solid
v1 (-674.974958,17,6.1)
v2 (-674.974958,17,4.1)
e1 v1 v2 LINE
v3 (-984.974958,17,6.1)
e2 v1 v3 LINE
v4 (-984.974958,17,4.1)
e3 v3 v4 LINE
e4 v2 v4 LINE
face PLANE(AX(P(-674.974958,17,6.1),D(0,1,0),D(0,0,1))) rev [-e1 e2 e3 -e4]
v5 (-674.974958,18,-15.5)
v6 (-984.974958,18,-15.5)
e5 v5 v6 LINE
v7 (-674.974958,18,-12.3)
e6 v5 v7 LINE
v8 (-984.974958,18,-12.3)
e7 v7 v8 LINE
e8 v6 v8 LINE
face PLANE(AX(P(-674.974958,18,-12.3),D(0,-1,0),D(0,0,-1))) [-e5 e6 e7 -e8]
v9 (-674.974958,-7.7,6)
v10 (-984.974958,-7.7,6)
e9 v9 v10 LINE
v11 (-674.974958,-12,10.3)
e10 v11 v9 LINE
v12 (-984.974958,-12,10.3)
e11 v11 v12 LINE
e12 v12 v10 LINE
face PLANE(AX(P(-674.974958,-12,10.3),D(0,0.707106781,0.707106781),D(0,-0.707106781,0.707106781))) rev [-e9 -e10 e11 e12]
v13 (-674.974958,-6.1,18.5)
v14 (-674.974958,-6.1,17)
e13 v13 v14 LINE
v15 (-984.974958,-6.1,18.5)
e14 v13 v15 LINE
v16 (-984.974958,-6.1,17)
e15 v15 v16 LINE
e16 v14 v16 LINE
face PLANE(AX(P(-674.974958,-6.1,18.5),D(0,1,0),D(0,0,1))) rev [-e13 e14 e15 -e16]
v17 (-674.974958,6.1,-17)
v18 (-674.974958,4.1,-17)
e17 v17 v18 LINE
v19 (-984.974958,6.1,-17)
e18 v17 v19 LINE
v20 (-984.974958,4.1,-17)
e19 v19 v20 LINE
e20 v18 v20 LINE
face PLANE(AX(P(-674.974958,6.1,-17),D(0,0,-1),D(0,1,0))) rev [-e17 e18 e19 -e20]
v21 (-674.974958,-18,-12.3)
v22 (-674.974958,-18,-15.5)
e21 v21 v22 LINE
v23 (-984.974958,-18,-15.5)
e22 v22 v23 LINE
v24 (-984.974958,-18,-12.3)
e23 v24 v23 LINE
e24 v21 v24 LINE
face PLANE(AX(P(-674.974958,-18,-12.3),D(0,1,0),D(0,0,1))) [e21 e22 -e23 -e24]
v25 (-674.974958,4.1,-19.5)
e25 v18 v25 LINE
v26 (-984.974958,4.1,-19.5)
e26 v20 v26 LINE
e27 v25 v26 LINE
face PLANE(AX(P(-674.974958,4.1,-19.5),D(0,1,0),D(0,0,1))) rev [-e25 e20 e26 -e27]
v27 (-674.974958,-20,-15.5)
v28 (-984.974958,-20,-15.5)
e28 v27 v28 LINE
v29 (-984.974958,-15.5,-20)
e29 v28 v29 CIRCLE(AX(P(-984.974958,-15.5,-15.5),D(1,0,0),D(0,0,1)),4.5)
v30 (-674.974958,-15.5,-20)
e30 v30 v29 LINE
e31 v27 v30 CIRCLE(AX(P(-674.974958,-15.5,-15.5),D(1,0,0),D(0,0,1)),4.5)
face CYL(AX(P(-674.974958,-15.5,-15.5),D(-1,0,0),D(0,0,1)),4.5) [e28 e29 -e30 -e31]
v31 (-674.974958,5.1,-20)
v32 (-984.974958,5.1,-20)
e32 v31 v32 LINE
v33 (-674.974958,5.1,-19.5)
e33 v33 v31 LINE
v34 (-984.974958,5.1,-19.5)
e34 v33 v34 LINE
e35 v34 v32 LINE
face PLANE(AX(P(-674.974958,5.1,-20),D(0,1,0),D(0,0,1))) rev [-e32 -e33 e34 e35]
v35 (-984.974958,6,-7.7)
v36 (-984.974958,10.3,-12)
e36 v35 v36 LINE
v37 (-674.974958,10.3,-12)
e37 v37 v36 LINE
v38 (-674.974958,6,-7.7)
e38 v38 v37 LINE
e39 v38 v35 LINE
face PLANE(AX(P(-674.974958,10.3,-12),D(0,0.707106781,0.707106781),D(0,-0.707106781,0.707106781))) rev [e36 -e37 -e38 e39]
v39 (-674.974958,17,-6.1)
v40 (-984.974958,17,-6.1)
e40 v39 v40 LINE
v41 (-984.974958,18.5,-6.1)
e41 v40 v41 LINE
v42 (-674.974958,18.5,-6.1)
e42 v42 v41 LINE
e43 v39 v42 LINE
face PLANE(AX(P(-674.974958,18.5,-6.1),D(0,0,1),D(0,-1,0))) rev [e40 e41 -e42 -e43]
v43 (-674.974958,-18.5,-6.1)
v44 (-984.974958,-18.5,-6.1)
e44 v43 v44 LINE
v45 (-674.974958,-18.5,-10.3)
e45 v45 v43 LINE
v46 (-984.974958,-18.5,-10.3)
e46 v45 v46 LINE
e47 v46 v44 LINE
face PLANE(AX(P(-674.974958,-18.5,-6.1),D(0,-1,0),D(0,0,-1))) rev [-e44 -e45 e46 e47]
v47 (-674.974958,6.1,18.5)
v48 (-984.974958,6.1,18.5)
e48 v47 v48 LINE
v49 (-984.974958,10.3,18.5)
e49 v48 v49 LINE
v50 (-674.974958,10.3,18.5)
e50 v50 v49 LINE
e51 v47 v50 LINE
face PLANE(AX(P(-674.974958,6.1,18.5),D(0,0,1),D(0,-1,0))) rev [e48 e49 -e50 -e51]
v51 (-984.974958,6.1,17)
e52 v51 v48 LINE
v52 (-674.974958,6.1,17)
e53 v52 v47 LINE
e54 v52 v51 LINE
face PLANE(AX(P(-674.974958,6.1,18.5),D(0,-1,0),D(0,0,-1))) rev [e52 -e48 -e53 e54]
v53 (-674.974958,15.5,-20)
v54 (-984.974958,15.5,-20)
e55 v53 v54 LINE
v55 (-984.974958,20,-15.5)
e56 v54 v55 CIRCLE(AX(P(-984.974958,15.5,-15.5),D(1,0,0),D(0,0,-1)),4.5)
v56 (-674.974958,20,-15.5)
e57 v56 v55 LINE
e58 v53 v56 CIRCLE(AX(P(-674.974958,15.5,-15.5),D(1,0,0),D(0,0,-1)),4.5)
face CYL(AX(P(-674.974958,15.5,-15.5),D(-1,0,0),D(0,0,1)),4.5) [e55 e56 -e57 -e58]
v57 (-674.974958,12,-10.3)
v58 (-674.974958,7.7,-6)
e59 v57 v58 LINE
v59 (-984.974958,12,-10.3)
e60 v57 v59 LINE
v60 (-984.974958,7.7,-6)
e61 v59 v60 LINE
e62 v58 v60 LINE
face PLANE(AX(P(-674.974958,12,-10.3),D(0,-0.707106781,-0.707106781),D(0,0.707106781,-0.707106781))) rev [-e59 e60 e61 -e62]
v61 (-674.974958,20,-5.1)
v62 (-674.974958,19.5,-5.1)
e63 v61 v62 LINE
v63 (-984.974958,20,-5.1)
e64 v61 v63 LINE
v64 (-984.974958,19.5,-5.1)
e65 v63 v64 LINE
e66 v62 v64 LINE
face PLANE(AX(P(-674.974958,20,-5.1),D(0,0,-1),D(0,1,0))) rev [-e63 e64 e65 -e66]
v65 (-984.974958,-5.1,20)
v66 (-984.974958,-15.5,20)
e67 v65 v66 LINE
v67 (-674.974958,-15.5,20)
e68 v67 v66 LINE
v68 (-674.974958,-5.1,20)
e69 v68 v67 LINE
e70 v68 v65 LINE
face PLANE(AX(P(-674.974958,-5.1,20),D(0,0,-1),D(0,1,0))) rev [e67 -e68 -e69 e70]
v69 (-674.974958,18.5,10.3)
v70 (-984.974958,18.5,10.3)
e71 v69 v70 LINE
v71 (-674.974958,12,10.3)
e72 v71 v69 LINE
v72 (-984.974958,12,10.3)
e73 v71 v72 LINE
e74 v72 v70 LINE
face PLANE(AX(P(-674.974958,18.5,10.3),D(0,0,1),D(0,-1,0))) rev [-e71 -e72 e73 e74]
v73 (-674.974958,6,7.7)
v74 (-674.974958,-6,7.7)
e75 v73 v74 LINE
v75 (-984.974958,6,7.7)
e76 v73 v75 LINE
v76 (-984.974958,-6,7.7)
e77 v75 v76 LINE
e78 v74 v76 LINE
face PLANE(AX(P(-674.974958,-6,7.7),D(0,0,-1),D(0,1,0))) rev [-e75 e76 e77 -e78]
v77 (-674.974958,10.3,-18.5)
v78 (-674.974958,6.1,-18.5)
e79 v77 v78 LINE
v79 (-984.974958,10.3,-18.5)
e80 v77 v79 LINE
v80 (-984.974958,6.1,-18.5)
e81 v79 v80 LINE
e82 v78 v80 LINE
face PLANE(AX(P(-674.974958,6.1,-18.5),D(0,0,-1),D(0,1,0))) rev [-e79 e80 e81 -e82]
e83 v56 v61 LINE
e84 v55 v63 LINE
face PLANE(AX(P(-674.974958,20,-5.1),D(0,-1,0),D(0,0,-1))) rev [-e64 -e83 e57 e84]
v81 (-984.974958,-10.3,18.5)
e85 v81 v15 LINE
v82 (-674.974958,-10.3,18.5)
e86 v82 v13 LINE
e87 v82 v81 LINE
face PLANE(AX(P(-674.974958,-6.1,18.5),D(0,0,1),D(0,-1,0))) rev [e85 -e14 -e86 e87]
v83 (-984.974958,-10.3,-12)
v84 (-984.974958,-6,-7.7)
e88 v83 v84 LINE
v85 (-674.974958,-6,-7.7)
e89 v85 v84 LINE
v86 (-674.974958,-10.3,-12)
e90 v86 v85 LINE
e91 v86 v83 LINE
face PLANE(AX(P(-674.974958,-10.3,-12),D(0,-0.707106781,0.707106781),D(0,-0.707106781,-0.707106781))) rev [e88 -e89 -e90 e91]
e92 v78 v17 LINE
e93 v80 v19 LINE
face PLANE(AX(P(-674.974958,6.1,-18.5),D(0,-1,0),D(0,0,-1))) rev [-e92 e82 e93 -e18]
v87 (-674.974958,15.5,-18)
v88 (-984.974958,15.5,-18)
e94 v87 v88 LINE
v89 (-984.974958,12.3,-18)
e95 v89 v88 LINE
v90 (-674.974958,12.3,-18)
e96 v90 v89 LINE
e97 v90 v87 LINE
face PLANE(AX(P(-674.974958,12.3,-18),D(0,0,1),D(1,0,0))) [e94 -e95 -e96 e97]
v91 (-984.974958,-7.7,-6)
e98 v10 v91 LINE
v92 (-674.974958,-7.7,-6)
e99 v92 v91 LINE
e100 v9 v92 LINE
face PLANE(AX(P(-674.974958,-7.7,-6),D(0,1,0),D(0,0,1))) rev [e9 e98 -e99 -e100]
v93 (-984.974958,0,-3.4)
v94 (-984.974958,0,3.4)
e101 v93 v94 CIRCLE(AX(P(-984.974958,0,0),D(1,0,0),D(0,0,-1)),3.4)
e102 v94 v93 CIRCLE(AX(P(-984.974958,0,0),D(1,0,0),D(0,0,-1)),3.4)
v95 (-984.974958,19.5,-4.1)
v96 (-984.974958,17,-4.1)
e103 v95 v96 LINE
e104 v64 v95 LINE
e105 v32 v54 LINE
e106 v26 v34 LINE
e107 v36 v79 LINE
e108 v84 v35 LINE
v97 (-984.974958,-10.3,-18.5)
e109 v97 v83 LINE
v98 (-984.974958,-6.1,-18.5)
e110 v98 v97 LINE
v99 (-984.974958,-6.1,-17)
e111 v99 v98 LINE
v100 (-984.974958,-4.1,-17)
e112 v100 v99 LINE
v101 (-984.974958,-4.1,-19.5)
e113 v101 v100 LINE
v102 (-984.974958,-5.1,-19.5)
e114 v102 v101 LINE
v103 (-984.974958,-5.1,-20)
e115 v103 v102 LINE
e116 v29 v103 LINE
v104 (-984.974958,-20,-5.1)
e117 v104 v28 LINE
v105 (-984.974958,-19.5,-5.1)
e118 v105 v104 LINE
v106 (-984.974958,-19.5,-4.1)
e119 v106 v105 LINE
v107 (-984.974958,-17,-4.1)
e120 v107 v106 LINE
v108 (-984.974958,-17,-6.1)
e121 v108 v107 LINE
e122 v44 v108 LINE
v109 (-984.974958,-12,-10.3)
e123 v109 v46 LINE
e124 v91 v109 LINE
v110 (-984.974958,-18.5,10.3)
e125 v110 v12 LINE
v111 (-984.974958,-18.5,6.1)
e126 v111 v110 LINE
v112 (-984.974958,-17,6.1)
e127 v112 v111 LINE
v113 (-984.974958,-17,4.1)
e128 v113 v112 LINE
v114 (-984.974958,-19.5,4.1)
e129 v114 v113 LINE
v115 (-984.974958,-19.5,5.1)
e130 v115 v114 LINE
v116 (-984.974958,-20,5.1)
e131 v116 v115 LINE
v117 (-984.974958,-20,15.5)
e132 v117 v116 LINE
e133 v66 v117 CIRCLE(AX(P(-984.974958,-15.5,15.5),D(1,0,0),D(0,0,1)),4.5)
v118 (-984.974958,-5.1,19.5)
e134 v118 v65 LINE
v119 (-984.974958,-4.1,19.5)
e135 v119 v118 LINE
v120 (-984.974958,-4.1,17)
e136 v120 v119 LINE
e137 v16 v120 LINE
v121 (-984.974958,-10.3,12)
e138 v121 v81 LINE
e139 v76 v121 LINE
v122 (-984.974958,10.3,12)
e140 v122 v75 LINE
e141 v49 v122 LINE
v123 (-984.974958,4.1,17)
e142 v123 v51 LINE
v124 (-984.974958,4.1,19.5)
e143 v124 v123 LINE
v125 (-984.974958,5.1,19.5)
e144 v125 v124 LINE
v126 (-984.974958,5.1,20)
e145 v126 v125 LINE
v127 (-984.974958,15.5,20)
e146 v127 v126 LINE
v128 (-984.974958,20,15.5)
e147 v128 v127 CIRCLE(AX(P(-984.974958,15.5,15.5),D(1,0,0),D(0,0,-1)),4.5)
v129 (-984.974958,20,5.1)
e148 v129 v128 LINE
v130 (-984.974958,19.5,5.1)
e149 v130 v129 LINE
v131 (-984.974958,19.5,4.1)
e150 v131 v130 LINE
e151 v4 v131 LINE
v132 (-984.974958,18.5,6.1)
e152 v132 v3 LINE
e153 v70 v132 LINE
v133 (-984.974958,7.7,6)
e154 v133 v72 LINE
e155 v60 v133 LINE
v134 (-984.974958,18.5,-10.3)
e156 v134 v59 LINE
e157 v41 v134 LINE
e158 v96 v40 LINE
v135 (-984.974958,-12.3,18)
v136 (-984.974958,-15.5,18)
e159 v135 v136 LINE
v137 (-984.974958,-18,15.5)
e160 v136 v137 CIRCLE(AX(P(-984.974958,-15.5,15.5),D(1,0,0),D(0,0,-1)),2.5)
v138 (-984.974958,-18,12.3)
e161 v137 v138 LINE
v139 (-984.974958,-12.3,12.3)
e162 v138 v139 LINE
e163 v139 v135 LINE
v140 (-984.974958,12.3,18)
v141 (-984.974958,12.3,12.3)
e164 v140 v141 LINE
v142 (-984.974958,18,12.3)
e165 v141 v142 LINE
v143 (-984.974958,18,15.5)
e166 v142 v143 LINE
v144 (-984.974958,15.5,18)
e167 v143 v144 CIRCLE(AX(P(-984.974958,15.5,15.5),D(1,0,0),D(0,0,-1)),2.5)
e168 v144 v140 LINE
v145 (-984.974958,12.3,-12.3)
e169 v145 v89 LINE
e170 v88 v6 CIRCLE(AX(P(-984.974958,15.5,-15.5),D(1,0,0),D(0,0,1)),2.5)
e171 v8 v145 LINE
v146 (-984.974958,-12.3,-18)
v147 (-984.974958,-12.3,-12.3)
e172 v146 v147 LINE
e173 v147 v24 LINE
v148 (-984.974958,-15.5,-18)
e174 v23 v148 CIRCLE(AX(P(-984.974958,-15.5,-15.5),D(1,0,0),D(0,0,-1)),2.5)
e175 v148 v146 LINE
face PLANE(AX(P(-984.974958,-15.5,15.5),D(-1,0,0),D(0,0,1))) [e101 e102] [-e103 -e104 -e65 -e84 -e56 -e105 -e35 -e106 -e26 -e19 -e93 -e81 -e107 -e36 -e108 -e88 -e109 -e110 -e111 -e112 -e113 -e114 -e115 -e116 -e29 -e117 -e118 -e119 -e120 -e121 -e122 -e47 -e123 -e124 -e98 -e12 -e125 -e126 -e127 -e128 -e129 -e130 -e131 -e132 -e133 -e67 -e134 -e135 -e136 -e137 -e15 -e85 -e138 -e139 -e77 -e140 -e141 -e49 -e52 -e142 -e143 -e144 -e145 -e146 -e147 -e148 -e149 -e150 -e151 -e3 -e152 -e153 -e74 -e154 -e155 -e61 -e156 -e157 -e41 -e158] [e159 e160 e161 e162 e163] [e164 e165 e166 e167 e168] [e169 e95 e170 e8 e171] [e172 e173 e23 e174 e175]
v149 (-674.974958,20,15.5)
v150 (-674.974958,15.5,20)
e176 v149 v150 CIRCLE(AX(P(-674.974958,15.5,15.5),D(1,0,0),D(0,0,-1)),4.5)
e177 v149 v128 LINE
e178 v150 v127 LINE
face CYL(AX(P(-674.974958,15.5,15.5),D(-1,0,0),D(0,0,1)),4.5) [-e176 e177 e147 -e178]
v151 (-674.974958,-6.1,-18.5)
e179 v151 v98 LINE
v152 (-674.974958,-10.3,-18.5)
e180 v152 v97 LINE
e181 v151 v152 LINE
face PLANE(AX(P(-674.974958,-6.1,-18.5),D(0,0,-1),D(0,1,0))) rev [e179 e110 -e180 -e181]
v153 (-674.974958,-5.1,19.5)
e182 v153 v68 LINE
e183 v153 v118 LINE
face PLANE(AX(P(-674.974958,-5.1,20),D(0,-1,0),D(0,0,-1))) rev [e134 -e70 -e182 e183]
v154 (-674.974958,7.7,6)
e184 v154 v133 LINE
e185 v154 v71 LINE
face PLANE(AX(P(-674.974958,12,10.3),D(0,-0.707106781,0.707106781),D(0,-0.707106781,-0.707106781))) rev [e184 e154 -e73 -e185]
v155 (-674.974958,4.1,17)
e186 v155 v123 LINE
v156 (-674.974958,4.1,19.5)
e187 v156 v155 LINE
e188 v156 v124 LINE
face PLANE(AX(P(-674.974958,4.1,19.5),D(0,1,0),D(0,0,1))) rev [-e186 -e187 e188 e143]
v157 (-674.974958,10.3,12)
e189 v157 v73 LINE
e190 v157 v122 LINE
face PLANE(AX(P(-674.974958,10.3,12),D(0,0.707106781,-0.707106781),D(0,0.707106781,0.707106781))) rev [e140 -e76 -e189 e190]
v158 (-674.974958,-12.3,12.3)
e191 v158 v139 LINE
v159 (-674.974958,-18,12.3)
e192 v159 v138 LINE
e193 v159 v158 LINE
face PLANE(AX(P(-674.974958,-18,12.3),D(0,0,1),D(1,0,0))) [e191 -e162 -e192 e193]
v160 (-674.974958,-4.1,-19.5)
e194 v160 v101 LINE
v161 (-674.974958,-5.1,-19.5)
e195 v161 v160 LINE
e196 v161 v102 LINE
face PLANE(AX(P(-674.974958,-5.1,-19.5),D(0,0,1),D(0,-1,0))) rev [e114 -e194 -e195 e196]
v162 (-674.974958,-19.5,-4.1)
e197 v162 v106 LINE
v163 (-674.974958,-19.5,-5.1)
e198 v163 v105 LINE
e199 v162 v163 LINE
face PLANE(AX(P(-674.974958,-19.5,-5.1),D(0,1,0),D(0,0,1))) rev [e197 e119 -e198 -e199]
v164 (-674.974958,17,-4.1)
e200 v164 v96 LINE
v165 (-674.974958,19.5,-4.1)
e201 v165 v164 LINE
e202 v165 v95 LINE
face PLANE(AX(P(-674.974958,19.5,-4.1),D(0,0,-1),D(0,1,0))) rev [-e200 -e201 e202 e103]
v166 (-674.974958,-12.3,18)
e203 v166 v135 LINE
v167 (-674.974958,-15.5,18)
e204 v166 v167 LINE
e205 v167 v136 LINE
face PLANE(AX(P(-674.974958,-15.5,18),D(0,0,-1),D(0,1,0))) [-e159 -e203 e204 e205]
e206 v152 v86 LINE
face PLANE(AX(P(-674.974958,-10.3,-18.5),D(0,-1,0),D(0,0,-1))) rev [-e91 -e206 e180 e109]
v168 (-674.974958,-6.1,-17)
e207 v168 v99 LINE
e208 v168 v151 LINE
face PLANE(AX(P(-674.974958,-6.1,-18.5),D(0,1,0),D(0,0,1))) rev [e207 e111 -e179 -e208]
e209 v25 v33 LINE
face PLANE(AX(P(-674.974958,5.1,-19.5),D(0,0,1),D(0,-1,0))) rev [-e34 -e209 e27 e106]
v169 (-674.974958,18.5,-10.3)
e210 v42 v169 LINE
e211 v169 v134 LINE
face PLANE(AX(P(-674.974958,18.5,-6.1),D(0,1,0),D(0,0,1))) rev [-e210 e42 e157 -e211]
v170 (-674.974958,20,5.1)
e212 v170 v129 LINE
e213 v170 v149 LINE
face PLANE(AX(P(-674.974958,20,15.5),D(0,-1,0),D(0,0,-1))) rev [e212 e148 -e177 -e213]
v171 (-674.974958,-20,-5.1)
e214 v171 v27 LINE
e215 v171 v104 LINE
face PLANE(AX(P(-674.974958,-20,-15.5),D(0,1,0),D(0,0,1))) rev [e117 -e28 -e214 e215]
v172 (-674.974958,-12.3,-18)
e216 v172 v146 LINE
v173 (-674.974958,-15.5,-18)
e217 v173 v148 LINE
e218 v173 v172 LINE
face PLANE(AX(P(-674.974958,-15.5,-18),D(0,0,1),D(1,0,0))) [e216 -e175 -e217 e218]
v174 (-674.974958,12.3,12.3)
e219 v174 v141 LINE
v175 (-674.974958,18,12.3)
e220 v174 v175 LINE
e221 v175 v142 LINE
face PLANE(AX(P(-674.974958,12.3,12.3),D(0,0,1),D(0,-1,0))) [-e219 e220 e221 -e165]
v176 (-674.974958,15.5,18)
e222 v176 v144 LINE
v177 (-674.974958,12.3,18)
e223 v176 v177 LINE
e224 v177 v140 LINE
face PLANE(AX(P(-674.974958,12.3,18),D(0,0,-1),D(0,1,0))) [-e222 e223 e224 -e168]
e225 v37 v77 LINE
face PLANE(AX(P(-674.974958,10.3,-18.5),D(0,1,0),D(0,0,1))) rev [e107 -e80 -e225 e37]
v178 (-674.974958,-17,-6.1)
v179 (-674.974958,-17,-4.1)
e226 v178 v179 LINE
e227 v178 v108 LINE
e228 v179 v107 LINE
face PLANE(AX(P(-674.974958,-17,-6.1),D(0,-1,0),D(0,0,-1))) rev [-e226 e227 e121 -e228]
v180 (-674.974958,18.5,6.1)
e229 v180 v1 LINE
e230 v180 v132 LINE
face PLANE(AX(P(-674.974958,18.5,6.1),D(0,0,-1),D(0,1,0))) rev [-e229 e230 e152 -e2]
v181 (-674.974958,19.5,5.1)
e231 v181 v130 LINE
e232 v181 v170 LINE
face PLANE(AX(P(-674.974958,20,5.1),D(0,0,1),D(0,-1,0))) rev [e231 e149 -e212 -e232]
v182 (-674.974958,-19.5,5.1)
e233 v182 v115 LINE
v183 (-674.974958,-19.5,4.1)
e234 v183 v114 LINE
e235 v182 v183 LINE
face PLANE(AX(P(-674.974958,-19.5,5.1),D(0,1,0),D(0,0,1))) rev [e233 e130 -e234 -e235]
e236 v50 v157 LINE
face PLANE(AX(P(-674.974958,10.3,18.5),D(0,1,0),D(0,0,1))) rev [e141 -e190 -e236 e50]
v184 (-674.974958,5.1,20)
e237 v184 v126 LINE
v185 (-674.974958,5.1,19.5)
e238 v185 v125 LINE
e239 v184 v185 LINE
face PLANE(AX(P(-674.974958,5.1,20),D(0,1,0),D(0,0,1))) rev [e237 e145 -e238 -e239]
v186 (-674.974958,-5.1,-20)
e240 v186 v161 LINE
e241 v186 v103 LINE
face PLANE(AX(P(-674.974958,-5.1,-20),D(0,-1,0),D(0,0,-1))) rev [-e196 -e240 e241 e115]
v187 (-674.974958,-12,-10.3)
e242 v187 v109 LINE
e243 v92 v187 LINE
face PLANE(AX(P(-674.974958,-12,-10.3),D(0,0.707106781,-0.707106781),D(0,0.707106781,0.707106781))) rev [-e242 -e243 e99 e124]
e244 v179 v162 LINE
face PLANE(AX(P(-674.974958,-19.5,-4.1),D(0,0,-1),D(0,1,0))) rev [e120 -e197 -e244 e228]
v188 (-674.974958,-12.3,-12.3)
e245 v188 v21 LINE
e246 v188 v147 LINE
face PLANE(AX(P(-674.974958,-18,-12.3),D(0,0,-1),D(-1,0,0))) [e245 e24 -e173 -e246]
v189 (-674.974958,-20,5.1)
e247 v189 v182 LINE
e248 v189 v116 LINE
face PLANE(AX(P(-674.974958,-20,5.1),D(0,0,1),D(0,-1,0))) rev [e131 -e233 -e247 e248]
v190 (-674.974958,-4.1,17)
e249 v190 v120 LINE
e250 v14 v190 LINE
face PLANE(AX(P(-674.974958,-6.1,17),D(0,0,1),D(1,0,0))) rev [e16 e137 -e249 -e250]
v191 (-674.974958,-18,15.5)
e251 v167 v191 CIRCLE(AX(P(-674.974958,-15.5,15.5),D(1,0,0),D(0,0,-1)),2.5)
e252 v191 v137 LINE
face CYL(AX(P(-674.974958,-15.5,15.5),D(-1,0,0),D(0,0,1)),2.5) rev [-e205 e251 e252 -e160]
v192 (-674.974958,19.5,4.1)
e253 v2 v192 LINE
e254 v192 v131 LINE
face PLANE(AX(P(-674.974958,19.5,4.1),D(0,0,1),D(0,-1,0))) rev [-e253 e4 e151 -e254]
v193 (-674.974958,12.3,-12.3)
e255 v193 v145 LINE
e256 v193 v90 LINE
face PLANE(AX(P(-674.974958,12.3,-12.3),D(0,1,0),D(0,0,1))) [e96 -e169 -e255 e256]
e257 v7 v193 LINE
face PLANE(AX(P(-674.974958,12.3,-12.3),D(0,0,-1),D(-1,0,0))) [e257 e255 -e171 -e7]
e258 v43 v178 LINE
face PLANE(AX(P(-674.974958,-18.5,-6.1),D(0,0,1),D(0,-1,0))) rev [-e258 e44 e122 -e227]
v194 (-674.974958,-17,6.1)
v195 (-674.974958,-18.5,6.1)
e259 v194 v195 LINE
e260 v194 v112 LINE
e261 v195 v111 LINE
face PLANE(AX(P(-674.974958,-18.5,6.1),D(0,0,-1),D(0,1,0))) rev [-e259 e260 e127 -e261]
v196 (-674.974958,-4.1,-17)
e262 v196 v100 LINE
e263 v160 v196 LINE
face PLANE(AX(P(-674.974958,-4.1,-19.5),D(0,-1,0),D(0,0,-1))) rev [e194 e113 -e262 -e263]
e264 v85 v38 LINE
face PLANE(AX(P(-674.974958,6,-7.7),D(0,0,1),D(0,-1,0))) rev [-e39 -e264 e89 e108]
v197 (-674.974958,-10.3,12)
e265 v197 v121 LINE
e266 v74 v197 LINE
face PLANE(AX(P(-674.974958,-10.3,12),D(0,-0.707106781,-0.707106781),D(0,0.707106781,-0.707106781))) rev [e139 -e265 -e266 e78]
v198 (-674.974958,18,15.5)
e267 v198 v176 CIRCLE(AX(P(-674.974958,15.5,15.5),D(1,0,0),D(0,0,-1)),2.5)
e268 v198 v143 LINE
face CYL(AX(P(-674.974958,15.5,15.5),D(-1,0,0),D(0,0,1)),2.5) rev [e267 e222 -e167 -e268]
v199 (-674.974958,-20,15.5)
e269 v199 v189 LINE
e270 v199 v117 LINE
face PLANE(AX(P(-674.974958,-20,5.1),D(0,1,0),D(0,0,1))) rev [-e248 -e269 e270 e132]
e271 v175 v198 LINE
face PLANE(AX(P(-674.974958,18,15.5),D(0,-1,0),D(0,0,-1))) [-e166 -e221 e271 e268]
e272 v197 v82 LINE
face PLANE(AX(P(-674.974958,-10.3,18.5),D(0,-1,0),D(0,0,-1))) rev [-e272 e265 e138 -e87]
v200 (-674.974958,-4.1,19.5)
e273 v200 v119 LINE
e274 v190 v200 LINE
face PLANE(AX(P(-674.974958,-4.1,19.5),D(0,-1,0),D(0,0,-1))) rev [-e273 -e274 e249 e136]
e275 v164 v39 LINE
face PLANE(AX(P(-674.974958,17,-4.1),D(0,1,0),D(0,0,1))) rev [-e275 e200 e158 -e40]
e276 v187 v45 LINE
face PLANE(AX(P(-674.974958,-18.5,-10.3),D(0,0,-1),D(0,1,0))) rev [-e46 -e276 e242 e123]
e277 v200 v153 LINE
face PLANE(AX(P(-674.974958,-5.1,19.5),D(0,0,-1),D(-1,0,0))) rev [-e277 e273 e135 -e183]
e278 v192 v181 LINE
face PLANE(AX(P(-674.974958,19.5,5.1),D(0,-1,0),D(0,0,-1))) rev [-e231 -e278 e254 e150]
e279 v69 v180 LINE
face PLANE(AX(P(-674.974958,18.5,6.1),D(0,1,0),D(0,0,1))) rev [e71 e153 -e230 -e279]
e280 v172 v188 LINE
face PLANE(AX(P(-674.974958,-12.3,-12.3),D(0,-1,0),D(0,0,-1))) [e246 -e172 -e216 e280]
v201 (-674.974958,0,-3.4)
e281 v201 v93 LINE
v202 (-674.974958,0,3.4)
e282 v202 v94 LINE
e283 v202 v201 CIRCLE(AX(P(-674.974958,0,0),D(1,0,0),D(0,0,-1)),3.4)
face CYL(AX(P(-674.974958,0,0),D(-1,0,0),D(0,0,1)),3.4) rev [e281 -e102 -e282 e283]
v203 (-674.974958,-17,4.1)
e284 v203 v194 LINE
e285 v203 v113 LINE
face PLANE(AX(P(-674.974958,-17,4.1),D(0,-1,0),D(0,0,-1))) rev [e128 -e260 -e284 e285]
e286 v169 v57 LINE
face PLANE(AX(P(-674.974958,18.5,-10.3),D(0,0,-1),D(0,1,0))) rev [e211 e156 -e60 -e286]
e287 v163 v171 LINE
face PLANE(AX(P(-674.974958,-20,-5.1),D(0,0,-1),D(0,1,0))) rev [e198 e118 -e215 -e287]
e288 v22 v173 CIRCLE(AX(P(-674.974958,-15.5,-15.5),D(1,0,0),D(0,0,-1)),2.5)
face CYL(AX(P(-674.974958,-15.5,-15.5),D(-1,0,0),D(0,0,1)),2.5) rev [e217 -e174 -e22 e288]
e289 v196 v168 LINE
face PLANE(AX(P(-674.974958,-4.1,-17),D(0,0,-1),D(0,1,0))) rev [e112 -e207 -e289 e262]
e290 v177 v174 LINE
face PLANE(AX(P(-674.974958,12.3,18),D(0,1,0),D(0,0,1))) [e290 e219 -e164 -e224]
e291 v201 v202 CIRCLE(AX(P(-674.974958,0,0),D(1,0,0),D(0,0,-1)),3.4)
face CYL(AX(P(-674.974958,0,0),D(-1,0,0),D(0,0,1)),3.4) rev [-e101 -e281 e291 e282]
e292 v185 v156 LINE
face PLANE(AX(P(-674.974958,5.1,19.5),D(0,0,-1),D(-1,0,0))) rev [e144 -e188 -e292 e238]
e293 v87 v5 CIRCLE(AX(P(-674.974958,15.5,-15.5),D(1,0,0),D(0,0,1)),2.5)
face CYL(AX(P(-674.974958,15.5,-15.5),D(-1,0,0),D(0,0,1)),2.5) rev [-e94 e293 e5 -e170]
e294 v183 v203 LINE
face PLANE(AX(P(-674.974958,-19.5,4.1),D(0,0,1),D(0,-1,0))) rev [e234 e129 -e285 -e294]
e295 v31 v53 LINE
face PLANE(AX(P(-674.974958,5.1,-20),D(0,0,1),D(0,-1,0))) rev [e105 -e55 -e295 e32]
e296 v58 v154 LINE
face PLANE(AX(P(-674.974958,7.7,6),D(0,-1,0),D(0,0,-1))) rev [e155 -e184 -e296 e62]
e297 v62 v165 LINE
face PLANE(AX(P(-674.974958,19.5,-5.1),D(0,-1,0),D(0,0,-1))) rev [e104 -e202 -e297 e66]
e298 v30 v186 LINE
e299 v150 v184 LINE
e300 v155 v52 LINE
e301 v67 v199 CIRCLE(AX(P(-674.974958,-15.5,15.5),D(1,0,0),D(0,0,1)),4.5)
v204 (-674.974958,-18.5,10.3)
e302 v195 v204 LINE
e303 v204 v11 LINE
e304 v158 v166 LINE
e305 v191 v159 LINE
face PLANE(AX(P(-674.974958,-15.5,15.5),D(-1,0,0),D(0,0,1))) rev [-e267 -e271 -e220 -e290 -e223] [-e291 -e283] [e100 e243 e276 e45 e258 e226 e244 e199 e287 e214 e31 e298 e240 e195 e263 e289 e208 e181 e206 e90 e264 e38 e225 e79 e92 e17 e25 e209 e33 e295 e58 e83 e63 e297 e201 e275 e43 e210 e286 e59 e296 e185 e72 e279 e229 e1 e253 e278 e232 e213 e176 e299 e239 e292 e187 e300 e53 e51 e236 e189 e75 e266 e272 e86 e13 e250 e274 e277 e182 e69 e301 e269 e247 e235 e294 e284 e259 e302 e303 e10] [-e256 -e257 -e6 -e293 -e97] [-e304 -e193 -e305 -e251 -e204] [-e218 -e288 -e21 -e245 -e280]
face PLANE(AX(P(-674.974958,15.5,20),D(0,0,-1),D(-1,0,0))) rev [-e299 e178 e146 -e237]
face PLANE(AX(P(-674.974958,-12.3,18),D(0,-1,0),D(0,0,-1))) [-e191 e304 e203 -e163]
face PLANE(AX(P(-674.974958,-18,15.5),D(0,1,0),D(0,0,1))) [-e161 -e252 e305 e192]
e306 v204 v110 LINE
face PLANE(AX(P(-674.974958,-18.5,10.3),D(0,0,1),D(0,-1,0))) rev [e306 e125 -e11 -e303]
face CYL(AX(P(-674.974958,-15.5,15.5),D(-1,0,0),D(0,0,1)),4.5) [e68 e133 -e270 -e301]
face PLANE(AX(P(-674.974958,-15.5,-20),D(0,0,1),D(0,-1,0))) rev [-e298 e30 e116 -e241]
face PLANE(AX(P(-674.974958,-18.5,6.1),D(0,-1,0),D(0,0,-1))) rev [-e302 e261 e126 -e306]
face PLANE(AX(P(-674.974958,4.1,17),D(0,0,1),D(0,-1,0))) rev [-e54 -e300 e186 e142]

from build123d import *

# Parameters (mm, degrees)
SKETCH1_R                                 = 3.4
ALUMINIUM_PROFILE_40_X_40B_X_R4_5_1_DEPTH = 310


with BuildPart() as part:
    # Sketch1 → Aluminium profile 40 X 40B X R4.5(1) (new body)
    with BuildSketch(Plane.YZ.offset(-984.974958264)):
        with BuildLine():
            Line((-5.1, 20), (-5.1, 19.5))
            Line((-5.1, 19.5), (-4.1, 19.5))
            Line((-4.1, 19.5), (-4.1, 17))
            Line((-4.1, 17), (-6.1, 17))
            Line((-6.1, 17), (-6.1, 18.5))
            Line((-6.1, 18.5), (-10.3, 18.5))
            Line((-10.3, 18.5), (-10.3, 12))
            Line((-10.3, 12), (-6, 7.7))
            Line((-6, 7.7), (6, 7.7))
            Line((6, 7.7), (10.3, 12))
            Line((10.3, 12), (10.3, 18.5))
            Line((10.3, 18.5), (6.1, 18.5))
            Line((6.1, 18.5), (6.1, 17))
            Line((6.1, 17), (4.1, 17))
            Line((4.1, 17), (4.1, 19.5))
            Line((4.1, 19.5), (5.1, 19.5))
            Line((5.1, 19.5), (5.1, 20))
            Line((5.1, 20), (15.5, 20))
            ThreePointArc((15.5, 20), (18.681980515, 18.681980515), (20, 15.5))
            Line((20, 15.5), (20, 5.1))
            Line((20, 5.1), (19.5, 5.1))
            Line((19.5, 5.1), (19.5, 4.1))
            Line((19.5, 4.1), (17, 4.1))
            Line((17, 4.1), (17, 6.1))
            Line((17, 6.1), (18.5, 6.1))
            Line((18.5, 6.1), (18.5, 10.3))
            Line((18.5, 10.3), (12, 10.3))
            Line((12, 10.3), (7.7, 6))
            Line((7.7, 6), (7.7, -6))
            Line((7.7, -6), (12, -10.3))
            Line((12, -10.3), (18.5, -10.3))
            Line((18.5, -10.3), (18.5, -6.1))
            Line((18.5, -6.1), (17, -6.1))
            Line((17, -6.1), (17, -4.1))
            Line((17, -4.1), (19.5, -4.1))
            Line((19.5, -4.1), (19.5, -5.1))
            Line((19.5, -5.1), (20, -5.1))
            Line((20, -5.1), (20, -15.5))
            ThreePointArc((20, -15.5), (18.681980515, -18.681980515), (15.5, -20))
            Line((15.5, -20), (5.1, -20))
            Line((5.1, -20), (5.1, -19.5))
            Line((5.1, -19.5), (4.1, -19.5))
            Line((4.1, -19.5), (4.1, -17))
            Line((4.1, -17), (6.1, -17))
            Line((6.1, -17), (6.1, -18.5))
            Line((6.1, -18.5), (10.3, -18.5))
            Line((10.3, -18.5), (10.3, -12))
            Line((10.3, -12), (6, -7.7))
            Line((6, -7.7), (-6, -7.7))
            Line((-6, -7.7), (-10.3, -12))
            Line((-10.3, -12), (-10.3, -18.5))
            Line((-10.3, -18.5), (-6.1, -18.5))
            Line((-6.1, -18.5), (-6.1, -17))
            Line((-6.1, -17), (-4.1, -17))
            Line((-4.1, -17), (-4.1, -19.5))
            Line((-4.1, -19.5), (-5.1, -19.5))
            Line((-5.1, -19.5), (-5.1, -20))
            Line((-5.1, -20), (-15.5, -20))
            ThreePointArc((-15.5, -20), (-18.681980515, -18.681980515), (-20, -15.5))
            Line((-20, -15.5), (-20, -5.1))
            Line((-20, -5.1), (-19.5, -5.1))
            Line((-19.5, -5.1), (-19.5, -4.1))
            Line((-19.5, -4.1), (-17, -4.1))
            Line((-17, -4.1), (-17, -6.1))
            Line((-17, -6.1), (-18.5, -6.1))
            Line((-18.5, -6.1), (-18.5, -10.3))
            Line((-18.5, -10.3), (-12, -10.3))
            Line((-12, -10.3), (-7.7, -6))
            Line((-7.7, -6), (-7.7, 6))
            Line((-7.7, 6), (-12, 10.3))
            Line((-12, 10.3), (-18.5, 10.3))
            Line((-18.5, 10.3), (-18.5, 6.1))
            Line((-18.5, 6.1), (-17, 6.1))
            Line((-17, 6.1), (-17, 4.1))
            Line((-17, 4.1), (-19.5, 4.1))
            Line((-19.5, 4.1), (-19.5, 5.1))
            Line((-19.5, 5.1), (-20, 5.1))
            Line((-20, 5.1), (-20, 15.5))
            ThreePointArc((-20, 15.5), (-18.681980515, 18.681980515), (-15.5, 20))
            Line((-15.5, 20), (-5.1, 20))
        make_face()
        Circle(SKETCH1_R, mode=Mode.SUBTRACT)
        with BuildLine():
            Line((12.3, 18), (15.5, 18))
            ThreePointArc((15.5, 18), (17.267766953, 17.267766953), (18, 15.5))
            Line((18, 15.5), (18, 12.3))
            Line((18, 12.3), (12.3, 12.3))
            Line((12.3, 12.3), (12.3, 18))
        make_face(mode=Mode.SUBTRACT)
        with BuildLine():
            Line((-15.5, 18), (-12.3, 18))
            Line((-12.3, 18), (-12.3, 12.3))
            Line((-12.3, 12.3), (-18, 12.3))
            Line((-18, 12.3), (-18, 15.5))
            ThreePointArc((-18, 15.5), (-17.267766953, 17.267766953), (-15.5, 18))
        make_face(mode=Mode.SUBTRACT)
        with BuildLine():
            Line((-18, -12.3), (-12.3, -12.3))
            Line((-12.3, -12.3), (-12.3, -18))
            Line((-12.3, -18), (-15.5, -18))
            ThreePointArc((-15.5, -18), (-17.267766953, -17.267766953), (-18, -15.5))
            Line((-18, -15.5), (-18, -12.3))
        make_face(mode=Mode.SUBTRACT)
        with BuildLine():
            Line((12.3, -12.3), (18, -12.3))
            Line((18, -12.3), (18, -15.5))
            ThreePointArc((18, -15.5), (17.267766953, -17.267766953), (15.5, -18))
            Line((15.5, -18), (12.3, -18))
            Line((12.3, -18), (12.3, -12.3))
        make_face(mode=Mode.SUBTRACT)
    extrude(amount=ALUMINIUM_PROFILE_40_X_40B_X_R4_5_1_DEPTH)


solid = part.part
